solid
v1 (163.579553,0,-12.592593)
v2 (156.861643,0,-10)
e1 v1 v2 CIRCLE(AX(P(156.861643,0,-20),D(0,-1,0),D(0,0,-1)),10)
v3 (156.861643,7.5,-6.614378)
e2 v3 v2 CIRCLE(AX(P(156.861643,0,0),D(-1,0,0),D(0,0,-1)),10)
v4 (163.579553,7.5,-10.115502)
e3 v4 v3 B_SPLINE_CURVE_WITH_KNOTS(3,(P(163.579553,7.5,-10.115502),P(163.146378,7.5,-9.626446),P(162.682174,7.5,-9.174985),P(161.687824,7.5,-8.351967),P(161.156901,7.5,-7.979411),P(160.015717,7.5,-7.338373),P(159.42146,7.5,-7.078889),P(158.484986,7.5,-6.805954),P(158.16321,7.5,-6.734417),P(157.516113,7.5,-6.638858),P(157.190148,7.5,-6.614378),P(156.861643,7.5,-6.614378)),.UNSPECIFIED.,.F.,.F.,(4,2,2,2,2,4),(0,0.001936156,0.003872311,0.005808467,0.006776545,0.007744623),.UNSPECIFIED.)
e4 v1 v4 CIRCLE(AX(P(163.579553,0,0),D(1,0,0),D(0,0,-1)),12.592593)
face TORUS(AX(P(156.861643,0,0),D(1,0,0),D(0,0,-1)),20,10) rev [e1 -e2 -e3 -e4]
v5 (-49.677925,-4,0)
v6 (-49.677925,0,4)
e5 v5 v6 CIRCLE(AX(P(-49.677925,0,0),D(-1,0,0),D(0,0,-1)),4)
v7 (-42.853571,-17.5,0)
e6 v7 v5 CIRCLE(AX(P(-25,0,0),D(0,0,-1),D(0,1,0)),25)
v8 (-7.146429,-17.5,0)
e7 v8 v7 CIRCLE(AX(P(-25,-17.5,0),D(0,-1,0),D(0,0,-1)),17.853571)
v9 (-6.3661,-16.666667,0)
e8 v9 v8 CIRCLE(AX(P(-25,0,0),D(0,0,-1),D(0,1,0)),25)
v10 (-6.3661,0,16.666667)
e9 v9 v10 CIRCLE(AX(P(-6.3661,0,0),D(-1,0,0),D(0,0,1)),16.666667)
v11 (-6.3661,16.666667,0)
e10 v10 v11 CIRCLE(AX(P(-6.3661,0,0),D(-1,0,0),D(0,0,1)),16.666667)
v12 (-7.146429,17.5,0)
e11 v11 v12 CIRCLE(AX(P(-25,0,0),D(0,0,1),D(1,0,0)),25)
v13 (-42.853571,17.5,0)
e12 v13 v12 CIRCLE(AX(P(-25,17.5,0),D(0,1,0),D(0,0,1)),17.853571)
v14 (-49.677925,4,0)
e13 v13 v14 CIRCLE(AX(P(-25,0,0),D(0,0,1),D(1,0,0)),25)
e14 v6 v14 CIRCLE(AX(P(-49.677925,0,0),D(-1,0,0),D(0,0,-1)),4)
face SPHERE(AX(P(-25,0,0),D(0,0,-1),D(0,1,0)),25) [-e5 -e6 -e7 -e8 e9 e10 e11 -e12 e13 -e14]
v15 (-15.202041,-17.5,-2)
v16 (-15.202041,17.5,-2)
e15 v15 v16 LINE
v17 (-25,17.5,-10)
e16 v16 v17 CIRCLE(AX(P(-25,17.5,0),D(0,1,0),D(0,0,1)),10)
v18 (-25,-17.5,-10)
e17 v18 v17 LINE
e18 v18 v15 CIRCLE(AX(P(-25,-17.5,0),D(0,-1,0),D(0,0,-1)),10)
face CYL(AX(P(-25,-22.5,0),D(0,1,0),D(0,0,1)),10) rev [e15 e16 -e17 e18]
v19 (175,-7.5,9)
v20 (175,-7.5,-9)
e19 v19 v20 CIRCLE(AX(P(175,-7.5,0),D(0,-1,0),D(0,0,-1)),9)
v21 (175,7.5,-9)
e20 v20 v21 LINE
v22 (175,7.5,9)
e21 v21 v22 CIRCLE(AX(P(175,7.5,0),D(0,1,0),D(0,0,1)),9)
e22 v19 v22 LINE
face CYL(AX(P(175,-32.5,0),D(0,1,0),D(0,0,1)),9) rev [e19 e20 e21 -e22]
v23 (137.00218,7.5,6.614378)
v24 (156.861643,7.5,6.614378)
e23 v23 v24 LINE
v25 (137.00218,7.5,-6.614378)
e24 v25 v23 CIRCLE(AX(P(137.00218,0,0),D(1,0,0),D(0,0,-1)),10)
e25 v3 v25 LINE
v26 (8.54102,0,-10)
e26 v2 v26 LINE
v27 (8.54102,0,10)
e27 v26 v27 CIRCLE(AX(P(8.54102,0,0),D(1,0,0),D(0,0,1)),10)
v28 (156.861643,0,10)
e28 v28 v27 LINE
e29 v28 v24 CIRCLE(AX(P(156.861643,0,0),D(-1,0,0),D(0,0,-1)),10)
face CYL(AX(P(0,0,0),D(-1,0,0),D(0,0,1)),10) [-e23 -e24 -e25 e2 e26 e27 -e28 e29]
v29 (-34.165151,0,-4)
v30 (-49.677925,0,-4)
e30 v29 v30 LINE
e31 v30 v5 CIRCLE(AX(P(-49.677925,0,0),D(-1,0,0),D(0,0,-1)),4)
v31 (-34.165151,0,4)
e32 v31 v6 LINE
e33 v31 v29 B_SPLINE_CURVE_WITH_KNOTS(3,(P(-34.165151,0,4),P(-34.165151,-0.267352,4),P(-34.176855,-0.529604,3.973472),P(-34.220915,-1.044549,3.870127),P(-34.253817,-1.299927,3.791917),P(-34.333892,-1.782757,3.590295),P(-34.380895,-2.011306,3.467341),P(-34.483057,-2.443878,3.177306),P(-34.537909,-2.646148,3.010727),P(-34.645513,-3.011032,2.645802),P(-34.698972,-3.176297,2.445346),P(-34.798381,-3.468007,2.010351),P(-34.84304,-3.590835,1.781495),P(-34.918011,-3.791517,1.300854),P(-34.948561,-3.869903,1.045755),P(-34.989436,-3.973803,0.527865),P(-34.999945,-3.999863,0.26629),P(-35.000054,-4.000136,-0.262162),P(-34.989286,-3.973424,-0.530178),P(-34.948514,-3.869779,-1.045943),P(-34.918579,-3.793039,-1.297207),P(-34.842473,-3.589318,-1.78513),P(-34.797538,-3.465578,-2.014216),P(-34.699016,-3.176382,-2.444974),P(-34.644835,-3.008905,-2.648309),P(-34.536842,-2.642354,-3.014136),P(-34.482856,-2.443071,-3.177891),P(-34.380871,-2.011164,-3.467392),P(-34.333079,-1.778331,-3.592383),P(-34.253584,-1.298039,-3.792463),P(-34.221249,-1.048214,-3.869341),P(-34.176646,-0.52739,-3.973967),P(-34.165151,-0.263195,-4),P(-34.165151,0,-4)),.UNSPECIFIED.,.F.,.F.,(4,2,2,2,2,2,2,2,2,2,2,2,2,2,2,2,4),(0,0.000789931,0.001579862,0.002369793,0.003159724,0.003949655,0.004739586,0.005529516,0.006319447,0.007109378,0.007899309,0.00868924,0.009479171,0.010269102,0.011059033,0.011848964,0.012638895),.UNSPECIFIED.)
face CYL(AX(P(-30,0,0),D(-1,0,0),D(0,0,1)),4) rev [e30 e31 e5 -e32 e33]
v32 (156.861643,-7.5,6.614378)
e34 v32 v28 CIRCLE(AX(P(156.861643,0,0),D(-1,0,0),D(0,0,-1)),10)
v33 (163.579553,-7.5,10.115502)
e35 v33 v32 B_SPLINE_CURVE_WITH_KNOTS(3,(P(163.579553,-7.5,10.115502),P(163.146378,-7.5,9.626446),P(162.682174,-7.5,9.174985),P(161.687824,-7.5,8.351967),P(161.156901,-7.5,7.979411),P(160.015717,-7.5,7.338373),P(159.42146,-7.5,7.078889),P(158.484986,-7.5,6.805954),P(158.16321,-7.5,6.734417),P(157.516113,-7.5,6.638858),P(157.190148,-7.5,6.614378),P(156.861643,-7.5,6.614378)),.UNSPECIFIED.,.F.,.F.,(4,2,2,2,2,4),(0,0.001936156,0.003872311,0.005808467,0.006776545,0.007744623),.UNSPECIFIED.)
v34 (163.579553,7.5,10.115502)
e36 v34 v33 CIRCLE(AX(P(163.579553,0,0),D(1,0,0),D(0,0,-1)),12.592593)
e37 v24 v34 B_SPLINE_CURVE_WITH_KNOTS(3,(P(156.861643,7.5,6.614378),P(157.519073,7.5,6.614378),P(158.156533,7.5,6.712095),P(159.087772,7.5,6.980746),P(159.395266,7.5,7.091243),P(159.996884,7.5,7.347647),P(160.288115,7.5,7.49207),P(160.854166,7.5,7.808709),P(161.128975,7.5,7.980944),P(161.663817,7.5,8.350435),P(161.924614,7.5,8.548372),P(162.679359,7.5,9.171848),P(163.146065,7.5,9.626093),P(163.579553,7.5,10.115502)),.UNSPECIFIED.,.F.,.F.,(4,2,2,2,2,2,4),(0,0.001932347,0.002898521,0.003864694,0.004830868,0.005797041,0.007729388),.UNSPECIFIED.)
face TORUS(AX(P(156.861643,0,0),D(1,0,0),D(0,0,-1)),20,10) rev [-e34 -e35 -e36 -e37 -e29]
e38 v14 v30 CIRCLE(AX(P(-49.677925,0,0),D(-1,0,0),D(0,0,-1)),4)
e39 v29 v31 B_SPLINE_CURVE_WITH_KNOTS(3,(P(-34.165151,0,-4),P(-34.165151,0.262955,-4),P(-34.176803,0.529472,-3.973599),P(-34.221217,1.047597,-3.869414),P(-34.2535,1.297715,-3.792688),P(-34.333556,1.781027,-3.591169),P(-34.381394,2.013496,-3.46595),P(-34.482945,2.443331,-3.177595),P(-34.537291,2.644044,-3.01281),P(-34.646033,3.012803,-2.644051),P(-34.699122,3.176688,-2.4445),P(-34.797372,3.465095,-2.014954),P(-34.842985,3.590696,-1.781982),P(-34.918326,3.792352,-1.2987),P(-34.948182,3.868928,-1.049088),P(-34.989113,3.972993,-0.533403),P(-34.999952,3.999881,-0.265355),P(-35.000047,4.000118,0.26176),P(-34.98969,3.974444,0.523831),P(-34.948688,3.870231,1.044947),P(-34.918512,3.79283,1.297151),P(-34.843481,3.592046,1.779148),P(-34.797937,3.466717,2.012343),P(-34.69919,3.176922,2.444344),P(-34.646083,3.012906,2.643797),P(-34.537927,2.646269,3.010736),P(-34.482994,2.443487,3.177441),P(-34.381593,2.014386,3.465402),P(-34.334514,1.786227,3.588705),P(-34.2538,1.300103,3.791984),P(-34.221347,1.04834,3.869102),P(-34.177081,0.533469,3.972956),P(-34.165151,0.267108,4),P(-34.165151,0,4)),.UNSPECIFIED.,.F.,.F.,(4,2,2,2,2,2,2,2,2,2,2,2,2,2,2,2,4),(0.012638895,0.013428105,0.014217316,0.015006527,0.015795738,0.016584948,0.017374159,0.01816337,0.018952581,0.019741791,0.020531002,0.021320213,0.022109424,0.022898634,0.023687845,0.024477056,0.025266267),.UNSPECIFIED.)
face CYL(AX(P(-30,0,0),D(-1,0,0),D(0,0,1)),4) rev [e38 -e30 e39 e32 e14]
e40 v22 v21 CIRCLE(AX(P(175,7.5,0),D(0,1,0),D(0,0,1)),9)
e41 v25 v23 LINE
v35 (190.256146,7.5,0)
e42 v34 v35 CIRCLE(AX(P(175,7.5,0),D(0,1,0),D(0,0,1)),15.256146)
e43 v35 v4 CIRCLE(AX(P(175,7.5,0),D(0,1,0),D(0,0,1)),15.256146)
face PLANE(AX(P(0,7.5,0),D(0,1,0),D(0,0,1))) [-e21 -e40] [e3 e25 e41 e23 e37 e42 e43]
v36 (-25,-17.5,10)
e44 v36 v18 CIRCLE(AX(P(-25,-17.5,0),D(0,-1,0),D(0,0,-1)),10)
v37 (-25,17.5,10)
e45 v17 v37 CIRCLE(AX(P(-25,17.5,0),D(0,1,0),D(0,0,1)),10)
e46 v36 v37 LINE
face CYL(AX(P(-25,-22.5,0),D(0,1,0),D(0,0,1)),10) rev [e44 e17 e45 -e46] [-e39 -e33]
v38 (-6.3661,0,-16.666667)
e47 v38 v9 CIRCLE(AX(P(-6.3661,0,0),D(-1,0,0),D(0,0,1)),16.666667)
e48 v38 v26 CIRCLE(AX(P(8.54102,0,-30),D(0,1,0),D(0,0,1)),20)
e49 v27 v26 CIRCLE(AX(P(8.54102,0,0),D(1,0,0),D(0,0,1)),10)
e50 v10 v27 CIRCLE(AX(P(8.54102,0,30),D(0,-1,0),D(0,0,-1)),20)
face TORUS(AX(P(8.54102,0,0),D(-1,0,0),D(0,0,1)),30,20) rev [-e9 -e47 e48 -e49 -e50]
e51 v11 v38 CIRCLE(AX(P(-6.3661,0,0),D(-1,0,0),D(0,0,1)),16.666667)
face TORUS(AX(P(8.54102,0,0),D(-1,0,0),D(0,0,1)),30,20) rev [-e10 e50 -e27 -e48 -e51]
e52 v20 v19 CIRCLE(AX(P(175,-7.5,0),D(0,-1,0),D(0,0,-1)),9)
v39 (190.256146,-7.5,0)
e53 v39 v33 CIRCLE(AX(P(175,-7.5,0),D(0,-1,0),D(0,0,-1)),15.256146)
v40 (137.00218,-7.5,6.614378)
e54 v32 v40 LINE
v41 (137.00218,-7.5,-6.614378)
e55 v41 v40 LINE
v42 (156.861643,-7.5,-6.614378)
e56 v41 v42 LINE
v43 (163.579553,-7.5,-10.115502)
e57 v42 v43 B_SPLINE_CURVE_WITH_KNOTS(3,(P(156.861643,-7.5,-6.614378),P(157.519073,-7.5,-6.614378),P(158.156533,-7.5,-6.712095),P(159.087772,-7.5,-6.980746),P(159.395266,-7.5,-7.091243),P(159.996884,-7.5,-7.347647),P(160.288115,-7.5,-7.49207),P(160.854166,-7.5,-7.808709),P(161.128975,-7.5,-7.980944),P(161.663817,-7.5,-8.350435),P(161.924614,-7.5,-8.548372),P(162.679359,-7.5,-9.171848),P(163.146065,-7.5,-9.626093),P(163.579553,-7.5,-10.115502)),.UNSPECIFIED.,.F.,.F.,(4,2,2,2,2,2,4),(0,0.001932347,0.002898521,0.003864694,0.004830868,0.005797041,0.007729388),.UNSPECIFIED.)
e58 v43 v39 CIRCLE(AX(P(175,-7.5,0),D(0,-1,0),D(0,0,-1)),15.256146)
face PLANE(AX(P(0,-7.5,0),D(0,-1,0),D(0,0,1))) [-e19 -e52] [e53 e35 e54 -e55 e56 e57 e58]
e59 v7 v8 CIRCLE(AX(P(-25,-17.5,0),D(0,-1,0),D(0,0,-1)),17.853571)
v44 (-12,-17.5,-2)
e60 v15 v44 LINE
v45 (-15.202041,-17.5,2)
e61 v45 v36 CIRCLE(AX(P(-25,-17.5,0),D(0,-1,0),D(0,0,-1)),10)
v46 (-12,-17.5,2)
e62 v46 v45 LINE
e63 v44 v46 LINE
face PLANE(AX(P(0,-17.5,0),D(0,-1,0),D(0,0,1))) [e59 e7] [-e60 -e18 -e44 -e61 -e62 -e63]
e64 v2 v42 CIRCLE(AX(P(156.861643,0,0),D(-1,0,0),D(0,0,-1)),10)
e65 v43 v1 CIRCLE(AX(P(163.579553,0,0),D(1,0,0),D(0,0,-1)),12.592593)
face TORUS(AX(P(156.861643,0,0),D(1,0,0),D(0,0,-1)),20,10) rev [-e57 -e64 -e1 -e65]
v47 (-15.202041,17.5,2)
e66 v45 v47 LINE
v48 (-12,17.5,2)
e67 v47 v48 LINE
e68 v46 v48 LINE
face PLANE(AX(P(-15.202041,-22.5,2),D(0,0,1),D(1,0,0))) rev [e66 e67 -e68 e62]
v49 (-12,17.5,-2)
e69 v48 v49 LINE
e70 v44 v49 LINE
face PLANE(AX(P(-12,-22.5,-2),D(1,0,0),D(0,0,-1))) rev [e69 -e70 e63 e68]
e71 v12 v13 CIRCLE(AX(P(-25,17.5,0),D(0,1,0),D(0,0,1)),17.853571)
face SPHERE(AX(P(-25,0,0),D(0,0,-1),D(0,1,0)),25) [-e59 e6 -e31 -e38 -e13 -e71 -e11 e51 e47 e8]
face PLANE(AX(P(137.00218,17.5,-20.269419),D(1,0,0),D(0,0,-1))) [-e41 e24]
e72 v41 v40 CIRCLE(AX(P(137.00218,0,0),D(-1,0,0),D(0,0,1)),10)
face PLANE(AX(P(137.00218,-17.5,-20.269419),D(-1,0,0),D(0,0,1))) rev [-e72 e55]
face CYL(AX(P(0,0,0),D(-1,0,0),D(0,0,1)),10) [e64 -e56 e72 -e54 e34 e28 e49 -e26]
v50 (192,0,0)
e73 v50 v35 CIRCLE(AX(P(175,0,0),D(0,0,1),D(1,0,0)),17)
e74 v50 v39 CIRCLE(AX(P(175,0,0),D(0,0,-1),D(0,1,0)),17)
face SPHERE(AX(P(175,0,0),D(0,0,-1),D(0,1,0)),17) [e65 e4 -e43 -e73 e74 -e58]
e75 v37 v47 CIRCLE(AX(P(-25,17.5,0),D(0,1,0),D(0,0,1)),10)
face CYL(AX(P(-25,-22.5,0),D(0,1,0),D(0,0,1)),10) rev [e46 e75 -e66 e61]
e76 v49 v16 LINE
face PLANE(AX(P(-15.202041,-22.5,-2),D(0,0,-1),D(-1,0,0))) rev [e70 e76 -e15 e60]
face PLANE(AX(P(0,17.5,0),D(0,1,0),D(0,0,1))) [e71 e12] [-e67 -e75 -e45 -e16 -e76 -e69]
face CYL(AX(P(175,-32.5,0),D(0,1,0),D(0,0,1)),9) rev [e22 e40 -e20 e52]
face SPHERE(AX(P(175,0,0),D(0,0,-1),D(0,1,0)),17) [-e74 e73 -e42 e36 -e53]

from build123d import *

# Parameters (mm, degrees)
SMALL_END_FLAT_DEPTH    = 10
BIG_END_FLAT_SKETCH_W   = 86.980428418
BIG_END_FLAT_SKETCH_H   = 55.493296348
BIG_END_FLAT_DEPTH      = 10
KEYED_BORE_20_DEPTH     = 40
SMALL_END_HOLE_SKETCH_R = 9
SMALL_END_HOLE_DEPTH    = 40
FILLET_R20_R            = 20
FILLET_R10_R            = 10
CROSS_HOLE_SKETCH_R     = 4
CROSS_HOLE_8_DEPTH      = 20


with BuildPart() as part:
    # Rod Profile Sketch → Rod Body Revolve (revolve)
    with BuildSketch(Plane.XY):
        with BuildLine():
            Line((-2.087121525, 10), (161.252272915, 10))
            ThreePointArc((161.252272915, 10), (180.257786585, 16.1664987), (192, 0))
            Line((192, 0), (-50, 0))
            ThreePointArc((-50, 0), (-30.107741092, 24.472657823), (-2.087121525, 10))
        make_face()
    revolve(axis=Axis((0, 0, 0), (1, 0, 0)))

    # Small End Flat Sketch → Small End Flat (cut)
    with BuildSketch(Plane(origin=(0, 7.5, 0), x_dir=(1, 0, 0), z_dir=(0, 1, 0))):
        Polygon((137.002179541, 20.26941877), (137.002179541, -16.521174788), (192.002179541, -16.521174788), (192.002179541, 18.008544306), align=None)
    small_end_flat = extrude(amount=SMALL_END_FLAT_DEPTH, mode=Mode.SUBTRACT)

    # Small End Flat Mirror: Small End Flat across plane
    add(small_end_flat.mirror(Plane.ZX), mode=Mode.SUBTRACT)

    # Big End Flat Sketch → Big End Flat (cut)
    with BuildSketch(Plane(origin=(0, 17.5, 0), x_dir=(1, 0, 0), z_dir=(0, 1, 0))):
        with Locations((-25, 0)):
            Rectangle(BIG_END_FLAT_SKETCH_W, BIG_END_FLAT_SKETCH_H)
    big_end_flat = extrude(amount=BIG_END_FLAT_DEPTH, mode=Mode.SUBTRACT)

    # Big End Flat Mirror: Big End Flat across plane
    add(big_end_flat.mirror(Plane.ZX), mode=Mode.SUBTRACT)

    # Keyed Bore Sketch → Keyed Bore Ø20 (cut)
    with BuildSketch(Plane(origin=(0, 17.5, 0), x_dir=(1, 0, 0), z_dir=(0, 1, 0))):
        with BuildLine():
            Line((-15.202041029, 2), (-12, 2))
            Line((-12, 2), (-12, -2))
            Line((-12, -2), (-15.202041029, -2))
            ThreePointArc((-15.202041029, -2), (-35, 0), (-15.202041029, 2))
        make_face()
    extrude(amount=-KEYED_BORE_20_DEPTH, mode=Mode.SUBTRACT)

    # Small End Hole Sketch → Small End Hole (cut)
    with BuildSketch(Plane(origin=(0, 7.5, 0), x_dir=(1, 0, 0), z_dir=(0, 1, 0))):
        with Locations(Location((175, 0, 0), (0, 0, 270))):
            Circle(SMALL_END_HOLE_SKETCH_R)
    extrude(amount=-SMALL_END_HOLE_DEPTH, mode=Mode.SUBTRACT)

    # Fillet R20
    fillet_r20_edges = [part.edges().sort_by_distance(p)[0] for p in [
        (-2.087121525, -10, 0),
    ]]
    fillet(fillet_r20_edges, radius=FILLET_R20_R)

    # Fillet R10
    fillet_r10_edges = [part.edges().sort_by_distance(p)[0] for p in [
        (161.252272915, 0, -10),
        (161.252272915, 0, 10),
    ]]
    fillet(fillet_r10_edges, radius=FILLET_R10_R)

    # Cross Hole Sketch → Cross Hole Ø8 (cut)
    with BuildSketch(Plane(origin=(-50, 0, 0), x_dir=(0, 0, -1), z_dir=(1, 0, 0))):
        with Locations(Location((0, 0, 0), (0, 0, 180))):
            Circle(CROSS_HOLE_SKETCH_R)
    extrude(amount=CROSS_HOLE_8_DEPTH, mode=Mode.SUBTRACT)


solid = part.part
